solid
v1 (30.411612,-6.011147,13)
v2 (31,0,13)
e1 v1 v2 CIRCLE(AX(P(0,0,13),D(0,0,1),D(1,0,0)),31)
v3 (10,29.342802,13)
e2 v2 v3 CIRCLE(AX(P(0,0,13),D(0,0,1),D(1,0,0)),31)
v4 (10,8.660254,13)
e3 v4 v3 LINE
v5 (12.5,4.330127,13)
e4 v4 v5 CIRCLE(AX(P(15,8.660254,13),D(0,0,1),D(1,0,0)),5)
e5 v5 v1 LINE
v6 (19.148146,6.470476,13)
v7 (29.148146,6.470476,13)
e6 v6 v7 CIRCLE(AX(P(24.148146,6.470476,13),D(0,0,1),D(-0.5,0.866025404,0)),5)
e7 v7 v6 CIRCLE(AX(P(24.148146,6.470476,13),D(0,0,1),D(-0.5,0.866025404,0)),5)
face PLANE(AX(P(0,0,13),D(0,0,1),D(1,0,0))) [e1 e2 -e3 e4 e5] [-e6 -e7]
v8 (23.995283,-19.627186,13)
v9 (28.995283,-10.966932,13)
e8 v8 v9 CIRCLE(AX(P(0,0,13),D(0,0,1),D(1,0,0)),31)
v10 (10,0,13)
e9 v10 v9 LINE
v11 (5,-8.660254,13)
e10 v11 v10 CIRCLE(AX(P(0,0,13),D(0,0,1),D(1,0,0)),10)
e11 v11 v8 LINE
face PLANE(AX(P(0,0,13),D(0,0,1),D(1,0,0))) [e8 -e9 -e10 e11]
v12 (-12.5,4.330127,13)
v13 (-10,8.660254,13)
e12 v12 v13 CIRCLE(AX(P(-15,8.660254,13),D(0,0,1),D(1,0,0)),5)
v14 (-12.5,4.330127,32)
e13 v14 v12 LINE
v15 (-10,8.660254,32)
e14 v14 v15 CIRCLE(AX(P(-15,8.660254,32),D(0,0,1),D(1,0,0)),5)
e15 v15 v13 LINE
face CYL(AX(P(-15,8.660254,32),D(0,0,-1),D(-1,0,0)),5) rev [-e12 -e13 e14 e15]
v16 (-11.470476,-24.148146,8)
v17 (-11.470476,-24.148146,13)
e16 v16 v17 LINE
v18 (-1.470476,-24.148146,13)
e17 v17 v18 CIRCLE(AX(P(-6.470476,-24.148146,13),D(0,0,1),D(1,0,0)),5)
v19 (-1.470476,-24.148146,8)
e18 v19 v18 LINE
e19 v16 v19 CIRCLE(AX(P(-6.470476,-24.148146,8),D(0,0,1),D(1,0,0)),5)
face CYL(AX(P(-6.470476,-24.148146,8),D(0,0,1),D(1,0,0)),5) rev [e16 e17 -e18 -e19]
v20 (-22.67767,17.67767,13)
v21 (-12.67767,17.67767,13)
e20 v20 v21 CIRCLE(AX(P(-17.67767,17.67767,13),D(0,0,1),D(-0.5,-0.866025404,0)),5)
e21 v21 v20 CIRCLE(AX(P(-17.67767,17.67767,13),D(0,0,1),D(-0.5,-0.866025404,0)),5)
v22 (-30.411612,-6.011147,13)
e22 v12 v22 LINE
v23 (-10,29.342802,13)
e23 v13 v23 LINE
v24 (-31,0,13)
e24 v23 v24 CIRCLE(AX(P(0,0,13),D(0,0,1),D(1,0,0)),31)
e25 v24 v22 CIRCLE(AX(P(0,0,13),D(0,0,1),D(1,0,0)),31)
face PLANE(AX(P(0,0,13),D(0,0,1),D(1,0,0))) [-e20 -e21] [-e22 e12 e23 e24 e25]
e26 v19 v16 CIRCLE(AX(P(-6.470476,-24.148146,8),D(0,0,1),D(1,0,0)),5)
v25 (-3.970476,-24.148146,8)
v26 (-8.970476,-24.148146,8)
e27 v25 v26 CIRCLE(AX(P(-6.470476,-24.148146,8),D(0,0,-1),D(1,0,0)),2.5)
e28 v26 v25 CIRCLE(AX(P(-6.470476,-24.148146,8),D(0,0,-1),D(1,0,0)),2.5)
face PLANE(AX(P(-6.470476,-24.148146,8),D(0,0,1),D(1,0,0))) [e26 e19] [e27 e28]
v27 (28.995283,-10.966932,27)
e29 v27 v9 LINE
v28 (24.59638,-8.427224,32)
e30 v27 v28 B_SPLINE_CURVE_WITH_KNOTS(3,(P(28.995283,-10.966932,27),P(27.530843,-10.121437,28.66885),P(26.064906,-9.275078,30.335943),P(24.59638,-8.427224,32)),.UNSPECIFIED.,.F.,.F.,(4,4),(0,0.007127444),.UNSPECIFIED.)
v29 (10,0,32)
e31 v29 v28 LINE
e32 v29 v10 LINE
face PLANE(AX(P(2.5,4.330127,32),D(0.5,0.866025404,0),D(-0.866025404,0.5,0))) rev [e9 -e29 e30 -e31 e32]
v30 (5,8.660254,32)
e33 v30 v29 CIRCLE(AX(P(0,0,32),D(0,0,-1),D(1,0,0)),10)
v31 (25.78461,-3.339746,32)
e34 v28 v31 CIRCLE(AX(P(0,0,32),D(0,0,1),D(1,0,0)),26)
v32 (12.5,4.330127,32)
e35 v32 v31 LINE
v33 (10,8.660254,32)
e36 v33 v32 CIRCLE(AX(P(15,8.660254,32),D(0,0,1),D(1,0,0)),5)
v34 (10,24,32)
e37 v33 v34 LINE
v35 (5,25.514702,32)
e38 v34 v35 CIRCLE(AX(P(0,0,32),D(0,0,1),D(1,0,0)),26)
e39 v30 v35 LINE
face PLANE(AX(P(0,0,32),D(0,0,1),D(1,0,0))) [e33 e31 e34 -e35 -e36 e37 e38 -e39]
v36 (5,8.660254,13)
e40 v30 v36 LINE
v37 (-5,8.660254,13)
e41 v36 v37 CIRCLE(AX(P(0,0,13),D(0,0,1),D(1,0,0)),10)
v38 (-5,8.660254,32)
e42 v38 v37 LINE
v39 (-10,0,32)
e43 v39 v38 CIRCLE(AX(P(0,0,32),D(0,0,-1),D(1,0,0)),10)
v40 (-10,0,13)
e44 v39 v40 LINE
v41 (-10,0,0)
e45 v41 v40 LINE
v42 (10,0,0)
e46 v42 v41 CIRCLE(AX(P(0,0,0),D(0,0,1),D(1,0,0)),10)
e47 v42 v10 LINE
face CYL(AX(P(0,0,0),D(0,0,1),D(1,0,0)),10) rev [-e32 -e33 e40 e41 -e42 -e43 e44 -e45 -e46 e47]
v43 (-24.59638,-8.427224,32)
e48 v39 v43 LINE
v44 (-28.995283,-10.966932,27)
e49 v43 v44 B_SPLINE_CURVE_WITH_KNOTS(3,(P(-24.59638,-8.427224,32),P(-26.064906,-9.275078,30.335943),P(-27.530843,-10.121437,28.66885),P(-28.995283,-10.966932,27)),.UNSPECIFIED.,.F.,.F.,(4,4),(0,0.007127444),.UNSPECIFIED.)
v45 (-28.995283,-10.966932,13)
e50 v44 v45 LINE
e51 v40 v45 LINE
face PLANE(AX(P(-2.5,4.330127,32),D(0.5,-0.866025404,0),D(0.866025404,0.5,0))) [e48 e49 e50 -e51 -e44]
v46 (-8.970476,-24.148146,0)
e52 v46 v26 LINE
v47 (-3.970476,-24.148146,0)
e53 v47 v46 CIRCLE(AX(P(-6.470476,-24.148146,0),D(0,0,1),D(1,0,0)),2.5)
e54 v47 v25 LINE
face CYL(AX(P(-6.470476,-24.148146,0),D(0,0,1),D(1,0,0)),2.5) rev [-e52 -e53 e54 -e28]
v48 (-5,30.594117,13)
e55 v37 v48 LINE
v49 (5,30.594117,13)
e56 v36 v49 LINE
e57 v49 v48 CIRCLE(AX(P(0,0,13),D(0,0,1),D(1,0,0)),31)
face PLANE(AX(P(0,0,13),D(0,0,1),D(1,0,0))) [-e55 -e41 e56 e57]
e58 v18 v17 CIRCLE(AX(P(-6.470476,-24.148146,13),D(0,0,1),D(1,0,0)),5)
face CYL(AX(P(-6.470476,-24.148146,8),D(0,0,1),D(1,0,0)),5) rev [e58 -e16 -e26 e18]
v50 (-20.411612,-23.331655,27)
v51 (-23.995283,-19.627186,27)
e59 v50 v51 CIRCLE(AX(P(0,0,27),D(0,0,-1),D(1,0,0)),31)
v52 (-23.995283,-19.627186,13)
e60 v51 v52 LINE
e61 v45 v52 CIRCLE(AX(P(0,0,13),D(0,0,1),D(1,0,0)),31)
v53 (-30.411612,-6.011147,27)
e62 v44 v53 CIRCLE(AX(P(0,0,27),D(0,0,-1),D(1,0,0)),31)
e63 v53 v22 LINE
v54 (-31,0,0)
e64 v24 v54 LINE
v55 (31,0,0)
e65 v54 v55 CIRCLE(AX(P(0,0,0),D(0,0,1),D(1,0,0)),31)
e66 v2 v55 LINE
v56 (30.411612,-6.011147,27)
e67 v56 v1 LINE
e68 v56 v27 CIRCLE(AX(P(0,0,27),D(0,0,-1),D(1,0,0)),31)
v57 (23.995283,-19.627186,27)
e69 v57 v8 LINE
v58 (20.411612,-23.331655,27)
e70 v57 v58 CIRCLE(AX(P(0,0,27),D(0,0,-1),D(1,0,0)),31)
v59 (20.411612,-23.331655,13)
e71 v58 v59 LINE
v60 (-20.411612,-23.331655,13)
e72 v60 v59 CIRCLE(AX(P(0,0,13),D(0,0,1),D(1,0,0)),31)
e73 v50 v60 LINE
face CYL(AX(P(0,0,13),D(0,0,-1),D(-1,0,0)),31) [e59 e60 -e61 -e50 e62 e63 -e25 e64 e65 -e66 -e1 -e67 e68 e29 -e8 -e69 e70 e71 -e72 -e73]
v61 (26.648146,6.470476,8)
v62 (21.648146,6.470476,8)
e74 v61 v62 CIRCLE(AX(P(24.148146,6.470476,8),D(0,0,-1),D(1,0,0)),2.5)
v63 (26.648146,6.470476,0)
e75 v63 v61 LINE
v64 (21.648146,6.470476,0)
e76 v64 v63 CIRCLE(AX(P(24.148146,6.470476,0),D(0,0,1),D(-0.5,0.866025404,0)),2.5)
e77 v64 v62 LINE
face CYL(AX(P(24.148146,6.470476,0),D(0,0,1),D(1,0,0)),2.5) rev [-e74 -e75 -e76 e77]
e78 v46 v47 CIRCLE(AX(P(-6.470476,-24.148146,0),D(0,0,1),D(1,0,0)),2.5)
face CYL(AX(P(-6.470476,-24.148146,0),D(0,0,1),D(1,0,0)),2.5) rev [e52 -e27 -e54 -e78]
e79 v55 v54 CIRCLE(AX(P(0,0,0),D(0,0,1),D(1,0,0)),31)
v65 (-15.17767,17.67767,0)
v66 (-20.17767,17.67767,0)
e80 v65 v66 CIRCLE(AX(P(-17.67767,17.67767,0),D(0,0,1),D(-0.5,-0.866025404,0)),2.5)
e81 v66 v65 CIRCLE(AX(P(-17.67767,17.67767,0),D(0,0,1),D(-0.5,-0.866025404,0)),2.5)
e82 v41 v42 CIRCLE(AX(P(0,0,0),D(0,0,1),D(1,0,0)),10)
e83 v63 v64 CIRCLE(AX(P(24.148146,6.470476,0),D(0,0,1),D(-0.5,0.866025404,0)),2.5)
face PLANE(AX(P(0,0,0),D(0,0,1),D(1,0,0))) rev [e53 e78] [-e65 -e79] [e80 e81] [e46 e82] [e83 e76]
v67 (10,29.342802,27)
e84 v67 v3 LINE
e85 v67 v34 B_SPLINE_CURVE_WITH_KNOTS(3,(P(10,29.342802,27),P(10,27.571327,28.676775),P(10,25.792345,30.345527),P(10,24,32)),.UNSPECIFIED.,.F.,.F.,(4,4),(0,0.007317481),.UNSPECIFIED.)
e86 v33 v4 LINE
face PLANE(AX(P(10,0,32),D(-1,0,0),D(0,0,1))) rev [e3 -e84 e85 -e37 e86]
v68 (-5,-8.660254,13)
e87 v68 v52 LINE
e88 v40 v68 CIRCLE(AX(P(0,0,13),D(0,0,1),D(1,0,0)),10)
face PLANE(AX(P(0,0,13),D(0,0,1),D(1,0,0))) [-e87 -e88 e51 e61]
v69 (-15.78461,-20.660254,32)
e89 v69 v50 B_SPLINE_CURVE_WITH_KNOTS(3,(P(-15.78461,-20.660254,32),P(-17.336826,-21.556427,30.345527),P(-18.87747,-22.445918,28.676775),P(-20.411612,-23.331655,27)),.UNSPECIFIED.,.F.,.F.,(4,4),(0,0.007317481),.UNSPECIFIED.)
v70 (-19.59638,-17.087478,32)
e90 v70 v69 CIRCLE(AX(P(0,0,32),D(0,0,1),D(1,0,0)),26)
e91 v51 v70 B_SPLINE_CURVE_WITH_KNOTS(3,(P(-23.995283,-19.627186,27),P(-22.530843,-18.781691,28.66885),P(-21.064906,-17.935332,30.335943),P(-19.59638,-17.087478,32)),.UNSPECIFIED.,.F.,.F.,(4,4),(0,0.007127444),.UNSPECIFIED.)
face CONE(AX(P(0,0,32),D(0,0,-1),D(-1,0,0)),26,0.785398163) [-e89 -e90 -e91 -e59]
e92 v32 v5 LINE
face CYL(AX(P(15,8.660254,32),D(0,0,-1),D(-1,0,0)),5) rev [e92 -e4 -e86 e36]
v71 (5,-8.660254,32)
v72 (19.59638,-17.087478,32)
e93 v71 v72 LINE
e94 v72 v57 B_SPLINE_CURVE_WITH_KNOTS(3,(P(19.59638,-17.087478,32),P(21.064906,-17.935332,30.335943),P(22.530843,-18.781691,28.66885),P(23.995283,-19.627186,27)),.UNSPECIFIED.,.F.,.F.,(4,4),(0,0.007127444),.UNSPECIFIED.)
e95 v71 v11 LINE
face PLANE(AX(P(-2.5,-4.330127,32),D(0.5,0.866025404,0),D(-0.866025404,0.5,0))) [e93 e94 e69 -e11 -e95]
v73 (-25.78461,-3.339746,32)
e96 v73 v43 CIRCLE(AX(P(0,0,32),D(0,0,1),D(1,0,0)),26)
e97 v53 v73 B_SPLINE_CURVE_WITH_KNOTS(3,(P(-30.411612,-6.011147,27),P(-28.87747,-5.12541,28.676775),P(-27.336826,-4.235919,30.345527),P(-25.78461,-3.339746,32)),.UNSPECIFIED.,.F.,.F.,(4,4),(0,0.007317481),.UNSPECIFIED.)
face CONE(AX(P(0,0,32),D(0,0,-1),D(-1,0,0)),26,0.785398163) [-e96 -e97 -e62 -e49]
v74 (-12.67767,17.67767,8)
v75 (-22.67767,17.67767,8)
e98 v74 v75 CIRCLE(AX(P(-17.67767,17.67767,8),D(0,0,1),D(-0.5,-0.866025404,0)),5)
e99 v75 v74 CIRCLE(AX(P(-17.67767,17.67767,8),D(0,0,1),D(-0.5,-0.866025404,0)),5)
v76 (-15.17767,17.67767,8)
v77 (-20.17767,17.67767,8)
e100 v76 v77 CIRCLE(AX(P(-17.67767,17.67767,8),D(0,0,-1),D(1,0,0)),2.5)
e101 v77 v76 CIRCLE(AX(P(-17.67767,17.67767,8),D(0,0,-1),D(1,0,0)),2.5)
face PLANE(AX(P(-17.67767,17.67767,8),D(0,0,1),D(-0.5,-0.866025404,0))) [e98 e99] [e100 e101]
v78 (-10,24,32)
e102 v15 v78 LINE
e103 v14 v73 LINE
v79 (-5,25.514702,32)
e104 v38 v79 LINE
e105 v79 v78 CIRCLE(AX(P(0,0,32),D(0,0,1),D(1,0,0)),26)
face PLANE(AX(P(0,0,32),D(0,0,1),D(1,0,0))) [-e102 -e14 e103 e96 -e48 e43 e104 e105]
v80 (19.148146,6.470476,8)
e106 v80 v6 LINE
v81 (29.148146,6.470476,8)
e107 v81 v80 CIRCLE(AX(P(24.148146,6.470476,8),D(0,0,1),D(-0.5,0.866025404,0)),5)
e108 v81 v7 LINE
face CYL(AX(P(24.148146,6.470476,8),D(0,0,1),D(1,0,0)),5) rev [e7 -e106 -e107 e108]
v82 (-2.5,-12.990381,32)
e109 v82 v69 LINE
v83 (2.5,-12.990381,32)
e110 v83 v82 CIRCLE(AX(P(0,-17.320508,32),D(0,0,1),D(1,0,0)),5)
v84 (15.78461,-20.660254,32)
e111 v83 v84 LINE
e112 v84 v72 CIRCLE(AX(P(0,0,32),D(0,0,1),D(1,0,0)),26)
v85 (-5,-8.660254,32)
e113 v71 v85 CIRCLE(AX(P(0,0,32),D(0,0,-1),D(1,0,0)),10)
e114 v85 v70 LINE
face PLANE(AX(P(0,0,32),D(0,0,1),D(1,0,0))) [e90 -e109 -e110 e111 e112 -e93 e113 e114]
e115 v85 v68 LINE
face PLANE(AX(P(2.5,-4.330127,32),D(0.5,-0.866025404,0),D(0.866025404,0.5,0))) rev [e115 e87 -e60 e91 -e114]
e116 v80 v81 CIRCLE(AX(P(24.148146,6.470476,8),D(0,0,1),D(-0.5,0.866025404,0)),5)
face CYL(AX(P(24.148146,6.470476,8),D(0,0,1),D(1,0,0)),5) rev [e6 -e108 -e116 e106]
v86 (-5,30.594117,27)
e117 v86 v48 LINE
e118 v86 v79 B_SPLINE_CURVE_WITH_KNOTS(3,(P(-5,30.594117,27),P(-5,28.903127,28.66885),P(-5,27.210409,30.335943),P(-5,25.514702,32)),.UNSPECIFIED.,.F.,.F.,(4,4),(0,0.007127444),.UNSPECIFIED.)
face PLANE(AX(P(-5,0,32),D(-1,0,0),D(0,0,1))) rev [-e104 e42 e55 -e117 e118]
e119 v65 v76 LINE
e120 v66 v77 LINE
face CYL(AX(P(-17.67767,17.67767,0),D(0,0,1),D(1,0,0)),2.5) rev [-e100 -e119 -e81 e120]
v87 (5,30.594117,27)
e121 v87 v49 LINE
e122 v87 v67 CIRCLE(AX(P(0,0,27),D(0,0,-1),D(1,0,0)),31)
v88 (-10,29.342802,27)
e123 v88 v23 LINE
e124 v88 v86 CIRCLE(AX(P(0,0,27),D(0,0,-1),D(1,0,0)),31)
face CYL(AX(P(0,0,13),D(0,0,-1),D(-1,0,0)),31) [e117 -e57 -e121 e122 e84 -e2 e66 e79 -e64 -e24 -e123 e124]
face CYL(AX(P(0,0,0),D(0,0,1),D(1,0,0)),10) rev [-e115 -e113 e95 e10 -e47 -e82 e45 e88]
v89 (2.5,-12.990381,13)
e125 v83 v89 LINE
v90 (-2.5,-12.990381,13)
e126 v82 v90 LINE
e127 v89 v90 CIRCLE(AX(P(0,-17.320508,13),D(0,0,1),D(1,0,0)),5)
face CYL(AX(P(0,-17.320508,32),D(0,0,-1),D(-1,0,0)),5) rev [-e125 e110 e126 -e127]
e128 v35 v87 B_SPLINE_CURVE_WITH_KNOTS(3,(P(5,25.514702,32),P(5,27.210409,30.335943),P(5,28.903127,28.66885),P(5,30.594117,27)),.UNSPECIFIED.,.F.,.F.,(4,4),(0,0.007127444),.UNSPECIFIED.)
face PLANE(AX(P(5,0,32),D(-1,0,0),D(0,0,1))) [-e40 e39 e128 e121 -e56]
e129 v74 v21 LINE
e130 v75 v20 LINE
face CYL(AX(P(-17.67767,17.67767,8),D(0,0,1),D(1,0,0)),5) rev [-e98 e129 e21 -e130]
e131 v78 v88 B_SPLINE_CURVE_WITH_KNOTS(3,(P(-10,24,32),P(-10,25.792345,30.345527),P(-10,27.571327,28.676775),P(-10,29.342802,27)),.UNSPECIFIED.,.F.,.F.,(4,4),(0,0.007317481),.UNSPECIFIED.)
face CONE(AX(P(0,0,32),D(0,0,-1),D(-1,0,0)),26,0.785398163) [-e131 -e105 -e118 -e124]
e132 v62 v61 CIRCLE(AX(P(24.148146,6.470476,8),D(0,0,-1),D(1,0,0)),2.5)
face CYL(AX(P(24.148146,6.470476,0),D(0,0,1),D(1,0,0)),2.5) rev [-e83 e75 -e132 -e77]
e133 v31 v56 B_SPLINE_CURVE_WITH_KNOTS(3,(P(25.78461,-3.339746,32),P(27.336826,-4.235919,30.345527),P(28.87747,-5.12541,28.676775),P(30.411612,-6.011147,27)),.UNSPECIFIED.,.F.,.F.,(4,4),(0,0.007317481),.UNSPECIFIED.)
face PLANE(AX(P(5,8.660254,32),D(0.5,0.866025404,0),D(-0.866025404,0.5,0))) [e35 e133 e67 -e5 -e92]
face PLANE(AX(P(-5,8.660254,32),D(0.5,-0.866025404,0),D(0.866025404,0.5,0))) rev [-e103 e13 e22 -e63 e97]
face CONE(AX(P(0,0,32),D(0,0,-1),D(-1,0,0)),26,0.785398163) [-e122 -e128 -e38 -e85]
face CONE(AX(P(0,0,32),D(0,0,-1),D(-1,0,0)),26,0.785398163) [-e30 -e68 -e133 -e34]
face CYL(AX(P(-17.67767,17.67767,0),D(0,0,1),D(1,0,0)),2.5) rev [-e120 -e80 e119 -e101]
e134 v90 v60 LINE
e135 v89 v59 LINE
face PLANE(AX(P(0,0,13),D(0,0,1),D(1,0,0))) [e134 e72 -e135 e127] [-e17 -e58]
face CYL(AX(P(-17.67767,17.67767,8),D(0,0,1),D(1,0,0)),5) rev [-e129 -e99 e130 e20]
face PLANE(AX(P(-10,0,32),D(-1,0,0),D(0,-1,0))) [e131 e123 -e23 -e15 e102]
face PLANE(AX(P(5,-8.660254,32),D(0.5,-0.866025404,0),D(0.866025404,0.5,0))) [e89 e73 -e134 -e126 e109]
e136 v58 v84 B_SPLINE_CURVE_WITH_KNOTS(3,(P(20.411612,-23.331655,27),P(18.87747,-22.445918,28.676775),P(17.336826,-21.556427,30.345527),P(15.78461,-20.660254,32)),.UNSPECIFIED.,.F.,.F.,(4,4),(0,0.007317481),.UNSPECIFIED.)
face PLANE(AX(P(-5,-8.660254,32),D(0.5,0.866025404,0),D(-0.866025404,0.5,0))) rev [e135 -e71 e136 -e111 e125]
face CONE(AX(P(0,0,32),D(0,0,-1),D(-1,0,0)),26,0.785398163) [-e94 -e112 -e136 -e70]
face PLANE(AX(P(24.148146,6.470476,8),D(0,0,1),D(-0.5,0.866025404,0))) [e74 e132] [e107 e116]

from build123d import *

# Parameters (mm, degrees)
BASE_DISC_SKETCH_R        = 31
BASE_DISC_62_DEPTH        = 13
RELIEF_CUT_SKETCH_R       = 10
RELIEF_CUT_DEPTH          = 46.727453461
THREE_ARM_BOSS_DEPTH      = 19
ARM_GAP_SKETCH_R          = 2.5
ARM_GAP_CUT_DEPTH         = 48.780749262
RADIAL_HOLE_SKETCH_R      = 5
RADIAL_HOLE_10_DEPTH      = 5
ARM_CUTS_PATTERN_3X_COUNT = 3
ARM_CHAMFERS_5MM_SIZE     = 5


with BuildPart() as part:
    # Base Disc Sketch → Base Disc Ø62 (new body)
    with BuildSketch(Plane.XY):
        with Locations(Location((0, 0, 0), (0, 0, 180))):
            Circle(BASE_DISC_SKETCH_R)
    extrude(amount=BASE_DISC_62_DEPTH)

    # Relief Cut Sketch → Relief Cut (cut, through all)
    with BuildSketch(Plane.XY.offset(13)):
        Circle(RELIEF_CUT_SKETCH_R)
    extrude(amount=-RELIEF_CUT_DEPTH, mode=Mode.SUBTRACT)

    # Arms Profile Sketch → Three-Arm Boss (add)
    with BuildSketch(Plane.XY.offset(13)):
        with BuildLine():
            Line((-5, 8.660254038), (-5, 30.594117082))
            ThreePointArc((-5, 30.594117082), (-7.526051267, 30.072554802), (-10, 29.342801502))
            Line((-10, 29.342801502), (-10, 8.660254038))
            ThreePointArc((-10, 8.660254038), (-10.669872981, 6.160254038), (-12.5, 4.330127019))
            Line((-12.5, 4.330127019), (-30.411611519, -6.011146713))
            ThreePointArc((-30.411611519, -6.011146713), (-29.806622049, -8.518525814), (-28.995282599, -10.966931522))
            Line((-28.995282599, -10.966931522), (-10, 0))
            ThreePointArc((-10, 0), (-8.660254038, 5), (-5, 8.660254038))
        make_face()
        with BuildLine():
            ThreePointArc((12.5, 4.330127019), (10.669872981, 6.160254038), (10, 8.660254038))
            Line((10, 8.660254038), (10, 29.342801502))
            ThreePointArc((10, 29.342801502), (7.526051267, 30.072554802), (5, 30.594117082))
            Line((5, 30.594117082), (5, 8.660254038))
            ThreePointArc((5, 8.660254038), (8.660254038, 5), (10, 0))
            Line((10, 0), (28.995282599, -10.966931522))
            ThreePointArc((28.995282599, -10.966931522), (29.806622049, -8.518525814), (30.411611519, -6.011146713))
            Line((30.411611519, -6.011146713), (12.5, 4.330127019))
        make_face()
        with BuildLine():
            ThreePointArc((20.411611519, -23.331654789), (22.280570782, -21.554028988), (23.995282599, -19.62718556))
            Line((23.995282599, -19.62718556), (5, -8.660254038))
            ThreePointArc((5, -8.660254038), (0, -10), (-5, -8.660254038))
            Line((-5, -8.660254038), (-23.995282599, -19.62718556))
            ThreePointArc((-23.995282599, -19.62718556), (-22.280570782, -21.554028988), (-20.411611519, -23.331654789))
            Line((-20.411611519, -23.331654789), (-2.5, -12.990381057))
            ThreePointArc((-2.5, -12.990381057), (0, -12.320508076), (2.5, -12.990381057))
            Line((2.5, -12.990381057), (20.411611519, -23.331654789))
        make_face()
    extrude(amount=THREE_ARM_BOSS_DEPTH)

    # Arm Gap Sketch → Arm Gap Cut (cut, through all)
    with BuildSketch(Plane.XY.offset(13)):
        with Locations((-6.470476128, -24.148145657)):
            Circle(ARM_GAP_SKETCH_R)
    arm_gap_cut = extrude(amount=-ARM_GAP_CUT_DEPTH, mode=Mode.SUBTRACT)

    # Radial Hole Sketch → Radial Hole Ø10 (cut)
    with BuildSketch(Plane.XY.offset(13)):
        with Locations((-6.470476128, -24.148145657)):
            Circle(RADIAL_HOLE_SKETCH_R)
    radial_hole_10 = extrude(amount=-RADIAL_HOLE_10_DEPTH, mode=Mode.SUBTRACT)

    # Arm Cuts Pattern 3x: Arm Gap Cut, Radial Hole Ø10 ×3 about axis
    arm_cuts_pattern_3x_axis = Axis((0, 0, 0), (0, 0, 1))
    add([arm_gap_cut.rotate(arm_cuts_pattern_3x_axis, i * 360 / ARM_CUTS_PATTERN_3X_COUNT) for i in range(1, ARM_CUTS_PATTERN_3X_COUNT)], mode=Mode.SUBTRACT)
    add([radial_hole_10.rotate(arm_cuts_pattern_3x_axis, i * 360 / ARM_CUTS_PATTERN_3X_COUNT) for i in range(1, ARM_CUTS_PATTERN_3X_COUNT)], mode=Mode.SUBTRACT)

    # Arm Chamfers 5mm
    arm_chamfers_5mm_edges = [part.edges().sort_by_distance(p)[0] for p in [
        (-29.806622049, -8.518525814, 32),
        (-7.526051267, 30.072554802, 32),
        (7.526051267, 30.072554802, 32),
        (29.806622049, -8.518525814, 32),
        (22.280570782, -21.554028988, 32),
        (-22.280570782, -21.554028988, 32),
    ]]
    chamfer(arm_chamfers_5mm_edges, length=ARM_CHAMFERS_5MM_SIZE)


solid = part.part
